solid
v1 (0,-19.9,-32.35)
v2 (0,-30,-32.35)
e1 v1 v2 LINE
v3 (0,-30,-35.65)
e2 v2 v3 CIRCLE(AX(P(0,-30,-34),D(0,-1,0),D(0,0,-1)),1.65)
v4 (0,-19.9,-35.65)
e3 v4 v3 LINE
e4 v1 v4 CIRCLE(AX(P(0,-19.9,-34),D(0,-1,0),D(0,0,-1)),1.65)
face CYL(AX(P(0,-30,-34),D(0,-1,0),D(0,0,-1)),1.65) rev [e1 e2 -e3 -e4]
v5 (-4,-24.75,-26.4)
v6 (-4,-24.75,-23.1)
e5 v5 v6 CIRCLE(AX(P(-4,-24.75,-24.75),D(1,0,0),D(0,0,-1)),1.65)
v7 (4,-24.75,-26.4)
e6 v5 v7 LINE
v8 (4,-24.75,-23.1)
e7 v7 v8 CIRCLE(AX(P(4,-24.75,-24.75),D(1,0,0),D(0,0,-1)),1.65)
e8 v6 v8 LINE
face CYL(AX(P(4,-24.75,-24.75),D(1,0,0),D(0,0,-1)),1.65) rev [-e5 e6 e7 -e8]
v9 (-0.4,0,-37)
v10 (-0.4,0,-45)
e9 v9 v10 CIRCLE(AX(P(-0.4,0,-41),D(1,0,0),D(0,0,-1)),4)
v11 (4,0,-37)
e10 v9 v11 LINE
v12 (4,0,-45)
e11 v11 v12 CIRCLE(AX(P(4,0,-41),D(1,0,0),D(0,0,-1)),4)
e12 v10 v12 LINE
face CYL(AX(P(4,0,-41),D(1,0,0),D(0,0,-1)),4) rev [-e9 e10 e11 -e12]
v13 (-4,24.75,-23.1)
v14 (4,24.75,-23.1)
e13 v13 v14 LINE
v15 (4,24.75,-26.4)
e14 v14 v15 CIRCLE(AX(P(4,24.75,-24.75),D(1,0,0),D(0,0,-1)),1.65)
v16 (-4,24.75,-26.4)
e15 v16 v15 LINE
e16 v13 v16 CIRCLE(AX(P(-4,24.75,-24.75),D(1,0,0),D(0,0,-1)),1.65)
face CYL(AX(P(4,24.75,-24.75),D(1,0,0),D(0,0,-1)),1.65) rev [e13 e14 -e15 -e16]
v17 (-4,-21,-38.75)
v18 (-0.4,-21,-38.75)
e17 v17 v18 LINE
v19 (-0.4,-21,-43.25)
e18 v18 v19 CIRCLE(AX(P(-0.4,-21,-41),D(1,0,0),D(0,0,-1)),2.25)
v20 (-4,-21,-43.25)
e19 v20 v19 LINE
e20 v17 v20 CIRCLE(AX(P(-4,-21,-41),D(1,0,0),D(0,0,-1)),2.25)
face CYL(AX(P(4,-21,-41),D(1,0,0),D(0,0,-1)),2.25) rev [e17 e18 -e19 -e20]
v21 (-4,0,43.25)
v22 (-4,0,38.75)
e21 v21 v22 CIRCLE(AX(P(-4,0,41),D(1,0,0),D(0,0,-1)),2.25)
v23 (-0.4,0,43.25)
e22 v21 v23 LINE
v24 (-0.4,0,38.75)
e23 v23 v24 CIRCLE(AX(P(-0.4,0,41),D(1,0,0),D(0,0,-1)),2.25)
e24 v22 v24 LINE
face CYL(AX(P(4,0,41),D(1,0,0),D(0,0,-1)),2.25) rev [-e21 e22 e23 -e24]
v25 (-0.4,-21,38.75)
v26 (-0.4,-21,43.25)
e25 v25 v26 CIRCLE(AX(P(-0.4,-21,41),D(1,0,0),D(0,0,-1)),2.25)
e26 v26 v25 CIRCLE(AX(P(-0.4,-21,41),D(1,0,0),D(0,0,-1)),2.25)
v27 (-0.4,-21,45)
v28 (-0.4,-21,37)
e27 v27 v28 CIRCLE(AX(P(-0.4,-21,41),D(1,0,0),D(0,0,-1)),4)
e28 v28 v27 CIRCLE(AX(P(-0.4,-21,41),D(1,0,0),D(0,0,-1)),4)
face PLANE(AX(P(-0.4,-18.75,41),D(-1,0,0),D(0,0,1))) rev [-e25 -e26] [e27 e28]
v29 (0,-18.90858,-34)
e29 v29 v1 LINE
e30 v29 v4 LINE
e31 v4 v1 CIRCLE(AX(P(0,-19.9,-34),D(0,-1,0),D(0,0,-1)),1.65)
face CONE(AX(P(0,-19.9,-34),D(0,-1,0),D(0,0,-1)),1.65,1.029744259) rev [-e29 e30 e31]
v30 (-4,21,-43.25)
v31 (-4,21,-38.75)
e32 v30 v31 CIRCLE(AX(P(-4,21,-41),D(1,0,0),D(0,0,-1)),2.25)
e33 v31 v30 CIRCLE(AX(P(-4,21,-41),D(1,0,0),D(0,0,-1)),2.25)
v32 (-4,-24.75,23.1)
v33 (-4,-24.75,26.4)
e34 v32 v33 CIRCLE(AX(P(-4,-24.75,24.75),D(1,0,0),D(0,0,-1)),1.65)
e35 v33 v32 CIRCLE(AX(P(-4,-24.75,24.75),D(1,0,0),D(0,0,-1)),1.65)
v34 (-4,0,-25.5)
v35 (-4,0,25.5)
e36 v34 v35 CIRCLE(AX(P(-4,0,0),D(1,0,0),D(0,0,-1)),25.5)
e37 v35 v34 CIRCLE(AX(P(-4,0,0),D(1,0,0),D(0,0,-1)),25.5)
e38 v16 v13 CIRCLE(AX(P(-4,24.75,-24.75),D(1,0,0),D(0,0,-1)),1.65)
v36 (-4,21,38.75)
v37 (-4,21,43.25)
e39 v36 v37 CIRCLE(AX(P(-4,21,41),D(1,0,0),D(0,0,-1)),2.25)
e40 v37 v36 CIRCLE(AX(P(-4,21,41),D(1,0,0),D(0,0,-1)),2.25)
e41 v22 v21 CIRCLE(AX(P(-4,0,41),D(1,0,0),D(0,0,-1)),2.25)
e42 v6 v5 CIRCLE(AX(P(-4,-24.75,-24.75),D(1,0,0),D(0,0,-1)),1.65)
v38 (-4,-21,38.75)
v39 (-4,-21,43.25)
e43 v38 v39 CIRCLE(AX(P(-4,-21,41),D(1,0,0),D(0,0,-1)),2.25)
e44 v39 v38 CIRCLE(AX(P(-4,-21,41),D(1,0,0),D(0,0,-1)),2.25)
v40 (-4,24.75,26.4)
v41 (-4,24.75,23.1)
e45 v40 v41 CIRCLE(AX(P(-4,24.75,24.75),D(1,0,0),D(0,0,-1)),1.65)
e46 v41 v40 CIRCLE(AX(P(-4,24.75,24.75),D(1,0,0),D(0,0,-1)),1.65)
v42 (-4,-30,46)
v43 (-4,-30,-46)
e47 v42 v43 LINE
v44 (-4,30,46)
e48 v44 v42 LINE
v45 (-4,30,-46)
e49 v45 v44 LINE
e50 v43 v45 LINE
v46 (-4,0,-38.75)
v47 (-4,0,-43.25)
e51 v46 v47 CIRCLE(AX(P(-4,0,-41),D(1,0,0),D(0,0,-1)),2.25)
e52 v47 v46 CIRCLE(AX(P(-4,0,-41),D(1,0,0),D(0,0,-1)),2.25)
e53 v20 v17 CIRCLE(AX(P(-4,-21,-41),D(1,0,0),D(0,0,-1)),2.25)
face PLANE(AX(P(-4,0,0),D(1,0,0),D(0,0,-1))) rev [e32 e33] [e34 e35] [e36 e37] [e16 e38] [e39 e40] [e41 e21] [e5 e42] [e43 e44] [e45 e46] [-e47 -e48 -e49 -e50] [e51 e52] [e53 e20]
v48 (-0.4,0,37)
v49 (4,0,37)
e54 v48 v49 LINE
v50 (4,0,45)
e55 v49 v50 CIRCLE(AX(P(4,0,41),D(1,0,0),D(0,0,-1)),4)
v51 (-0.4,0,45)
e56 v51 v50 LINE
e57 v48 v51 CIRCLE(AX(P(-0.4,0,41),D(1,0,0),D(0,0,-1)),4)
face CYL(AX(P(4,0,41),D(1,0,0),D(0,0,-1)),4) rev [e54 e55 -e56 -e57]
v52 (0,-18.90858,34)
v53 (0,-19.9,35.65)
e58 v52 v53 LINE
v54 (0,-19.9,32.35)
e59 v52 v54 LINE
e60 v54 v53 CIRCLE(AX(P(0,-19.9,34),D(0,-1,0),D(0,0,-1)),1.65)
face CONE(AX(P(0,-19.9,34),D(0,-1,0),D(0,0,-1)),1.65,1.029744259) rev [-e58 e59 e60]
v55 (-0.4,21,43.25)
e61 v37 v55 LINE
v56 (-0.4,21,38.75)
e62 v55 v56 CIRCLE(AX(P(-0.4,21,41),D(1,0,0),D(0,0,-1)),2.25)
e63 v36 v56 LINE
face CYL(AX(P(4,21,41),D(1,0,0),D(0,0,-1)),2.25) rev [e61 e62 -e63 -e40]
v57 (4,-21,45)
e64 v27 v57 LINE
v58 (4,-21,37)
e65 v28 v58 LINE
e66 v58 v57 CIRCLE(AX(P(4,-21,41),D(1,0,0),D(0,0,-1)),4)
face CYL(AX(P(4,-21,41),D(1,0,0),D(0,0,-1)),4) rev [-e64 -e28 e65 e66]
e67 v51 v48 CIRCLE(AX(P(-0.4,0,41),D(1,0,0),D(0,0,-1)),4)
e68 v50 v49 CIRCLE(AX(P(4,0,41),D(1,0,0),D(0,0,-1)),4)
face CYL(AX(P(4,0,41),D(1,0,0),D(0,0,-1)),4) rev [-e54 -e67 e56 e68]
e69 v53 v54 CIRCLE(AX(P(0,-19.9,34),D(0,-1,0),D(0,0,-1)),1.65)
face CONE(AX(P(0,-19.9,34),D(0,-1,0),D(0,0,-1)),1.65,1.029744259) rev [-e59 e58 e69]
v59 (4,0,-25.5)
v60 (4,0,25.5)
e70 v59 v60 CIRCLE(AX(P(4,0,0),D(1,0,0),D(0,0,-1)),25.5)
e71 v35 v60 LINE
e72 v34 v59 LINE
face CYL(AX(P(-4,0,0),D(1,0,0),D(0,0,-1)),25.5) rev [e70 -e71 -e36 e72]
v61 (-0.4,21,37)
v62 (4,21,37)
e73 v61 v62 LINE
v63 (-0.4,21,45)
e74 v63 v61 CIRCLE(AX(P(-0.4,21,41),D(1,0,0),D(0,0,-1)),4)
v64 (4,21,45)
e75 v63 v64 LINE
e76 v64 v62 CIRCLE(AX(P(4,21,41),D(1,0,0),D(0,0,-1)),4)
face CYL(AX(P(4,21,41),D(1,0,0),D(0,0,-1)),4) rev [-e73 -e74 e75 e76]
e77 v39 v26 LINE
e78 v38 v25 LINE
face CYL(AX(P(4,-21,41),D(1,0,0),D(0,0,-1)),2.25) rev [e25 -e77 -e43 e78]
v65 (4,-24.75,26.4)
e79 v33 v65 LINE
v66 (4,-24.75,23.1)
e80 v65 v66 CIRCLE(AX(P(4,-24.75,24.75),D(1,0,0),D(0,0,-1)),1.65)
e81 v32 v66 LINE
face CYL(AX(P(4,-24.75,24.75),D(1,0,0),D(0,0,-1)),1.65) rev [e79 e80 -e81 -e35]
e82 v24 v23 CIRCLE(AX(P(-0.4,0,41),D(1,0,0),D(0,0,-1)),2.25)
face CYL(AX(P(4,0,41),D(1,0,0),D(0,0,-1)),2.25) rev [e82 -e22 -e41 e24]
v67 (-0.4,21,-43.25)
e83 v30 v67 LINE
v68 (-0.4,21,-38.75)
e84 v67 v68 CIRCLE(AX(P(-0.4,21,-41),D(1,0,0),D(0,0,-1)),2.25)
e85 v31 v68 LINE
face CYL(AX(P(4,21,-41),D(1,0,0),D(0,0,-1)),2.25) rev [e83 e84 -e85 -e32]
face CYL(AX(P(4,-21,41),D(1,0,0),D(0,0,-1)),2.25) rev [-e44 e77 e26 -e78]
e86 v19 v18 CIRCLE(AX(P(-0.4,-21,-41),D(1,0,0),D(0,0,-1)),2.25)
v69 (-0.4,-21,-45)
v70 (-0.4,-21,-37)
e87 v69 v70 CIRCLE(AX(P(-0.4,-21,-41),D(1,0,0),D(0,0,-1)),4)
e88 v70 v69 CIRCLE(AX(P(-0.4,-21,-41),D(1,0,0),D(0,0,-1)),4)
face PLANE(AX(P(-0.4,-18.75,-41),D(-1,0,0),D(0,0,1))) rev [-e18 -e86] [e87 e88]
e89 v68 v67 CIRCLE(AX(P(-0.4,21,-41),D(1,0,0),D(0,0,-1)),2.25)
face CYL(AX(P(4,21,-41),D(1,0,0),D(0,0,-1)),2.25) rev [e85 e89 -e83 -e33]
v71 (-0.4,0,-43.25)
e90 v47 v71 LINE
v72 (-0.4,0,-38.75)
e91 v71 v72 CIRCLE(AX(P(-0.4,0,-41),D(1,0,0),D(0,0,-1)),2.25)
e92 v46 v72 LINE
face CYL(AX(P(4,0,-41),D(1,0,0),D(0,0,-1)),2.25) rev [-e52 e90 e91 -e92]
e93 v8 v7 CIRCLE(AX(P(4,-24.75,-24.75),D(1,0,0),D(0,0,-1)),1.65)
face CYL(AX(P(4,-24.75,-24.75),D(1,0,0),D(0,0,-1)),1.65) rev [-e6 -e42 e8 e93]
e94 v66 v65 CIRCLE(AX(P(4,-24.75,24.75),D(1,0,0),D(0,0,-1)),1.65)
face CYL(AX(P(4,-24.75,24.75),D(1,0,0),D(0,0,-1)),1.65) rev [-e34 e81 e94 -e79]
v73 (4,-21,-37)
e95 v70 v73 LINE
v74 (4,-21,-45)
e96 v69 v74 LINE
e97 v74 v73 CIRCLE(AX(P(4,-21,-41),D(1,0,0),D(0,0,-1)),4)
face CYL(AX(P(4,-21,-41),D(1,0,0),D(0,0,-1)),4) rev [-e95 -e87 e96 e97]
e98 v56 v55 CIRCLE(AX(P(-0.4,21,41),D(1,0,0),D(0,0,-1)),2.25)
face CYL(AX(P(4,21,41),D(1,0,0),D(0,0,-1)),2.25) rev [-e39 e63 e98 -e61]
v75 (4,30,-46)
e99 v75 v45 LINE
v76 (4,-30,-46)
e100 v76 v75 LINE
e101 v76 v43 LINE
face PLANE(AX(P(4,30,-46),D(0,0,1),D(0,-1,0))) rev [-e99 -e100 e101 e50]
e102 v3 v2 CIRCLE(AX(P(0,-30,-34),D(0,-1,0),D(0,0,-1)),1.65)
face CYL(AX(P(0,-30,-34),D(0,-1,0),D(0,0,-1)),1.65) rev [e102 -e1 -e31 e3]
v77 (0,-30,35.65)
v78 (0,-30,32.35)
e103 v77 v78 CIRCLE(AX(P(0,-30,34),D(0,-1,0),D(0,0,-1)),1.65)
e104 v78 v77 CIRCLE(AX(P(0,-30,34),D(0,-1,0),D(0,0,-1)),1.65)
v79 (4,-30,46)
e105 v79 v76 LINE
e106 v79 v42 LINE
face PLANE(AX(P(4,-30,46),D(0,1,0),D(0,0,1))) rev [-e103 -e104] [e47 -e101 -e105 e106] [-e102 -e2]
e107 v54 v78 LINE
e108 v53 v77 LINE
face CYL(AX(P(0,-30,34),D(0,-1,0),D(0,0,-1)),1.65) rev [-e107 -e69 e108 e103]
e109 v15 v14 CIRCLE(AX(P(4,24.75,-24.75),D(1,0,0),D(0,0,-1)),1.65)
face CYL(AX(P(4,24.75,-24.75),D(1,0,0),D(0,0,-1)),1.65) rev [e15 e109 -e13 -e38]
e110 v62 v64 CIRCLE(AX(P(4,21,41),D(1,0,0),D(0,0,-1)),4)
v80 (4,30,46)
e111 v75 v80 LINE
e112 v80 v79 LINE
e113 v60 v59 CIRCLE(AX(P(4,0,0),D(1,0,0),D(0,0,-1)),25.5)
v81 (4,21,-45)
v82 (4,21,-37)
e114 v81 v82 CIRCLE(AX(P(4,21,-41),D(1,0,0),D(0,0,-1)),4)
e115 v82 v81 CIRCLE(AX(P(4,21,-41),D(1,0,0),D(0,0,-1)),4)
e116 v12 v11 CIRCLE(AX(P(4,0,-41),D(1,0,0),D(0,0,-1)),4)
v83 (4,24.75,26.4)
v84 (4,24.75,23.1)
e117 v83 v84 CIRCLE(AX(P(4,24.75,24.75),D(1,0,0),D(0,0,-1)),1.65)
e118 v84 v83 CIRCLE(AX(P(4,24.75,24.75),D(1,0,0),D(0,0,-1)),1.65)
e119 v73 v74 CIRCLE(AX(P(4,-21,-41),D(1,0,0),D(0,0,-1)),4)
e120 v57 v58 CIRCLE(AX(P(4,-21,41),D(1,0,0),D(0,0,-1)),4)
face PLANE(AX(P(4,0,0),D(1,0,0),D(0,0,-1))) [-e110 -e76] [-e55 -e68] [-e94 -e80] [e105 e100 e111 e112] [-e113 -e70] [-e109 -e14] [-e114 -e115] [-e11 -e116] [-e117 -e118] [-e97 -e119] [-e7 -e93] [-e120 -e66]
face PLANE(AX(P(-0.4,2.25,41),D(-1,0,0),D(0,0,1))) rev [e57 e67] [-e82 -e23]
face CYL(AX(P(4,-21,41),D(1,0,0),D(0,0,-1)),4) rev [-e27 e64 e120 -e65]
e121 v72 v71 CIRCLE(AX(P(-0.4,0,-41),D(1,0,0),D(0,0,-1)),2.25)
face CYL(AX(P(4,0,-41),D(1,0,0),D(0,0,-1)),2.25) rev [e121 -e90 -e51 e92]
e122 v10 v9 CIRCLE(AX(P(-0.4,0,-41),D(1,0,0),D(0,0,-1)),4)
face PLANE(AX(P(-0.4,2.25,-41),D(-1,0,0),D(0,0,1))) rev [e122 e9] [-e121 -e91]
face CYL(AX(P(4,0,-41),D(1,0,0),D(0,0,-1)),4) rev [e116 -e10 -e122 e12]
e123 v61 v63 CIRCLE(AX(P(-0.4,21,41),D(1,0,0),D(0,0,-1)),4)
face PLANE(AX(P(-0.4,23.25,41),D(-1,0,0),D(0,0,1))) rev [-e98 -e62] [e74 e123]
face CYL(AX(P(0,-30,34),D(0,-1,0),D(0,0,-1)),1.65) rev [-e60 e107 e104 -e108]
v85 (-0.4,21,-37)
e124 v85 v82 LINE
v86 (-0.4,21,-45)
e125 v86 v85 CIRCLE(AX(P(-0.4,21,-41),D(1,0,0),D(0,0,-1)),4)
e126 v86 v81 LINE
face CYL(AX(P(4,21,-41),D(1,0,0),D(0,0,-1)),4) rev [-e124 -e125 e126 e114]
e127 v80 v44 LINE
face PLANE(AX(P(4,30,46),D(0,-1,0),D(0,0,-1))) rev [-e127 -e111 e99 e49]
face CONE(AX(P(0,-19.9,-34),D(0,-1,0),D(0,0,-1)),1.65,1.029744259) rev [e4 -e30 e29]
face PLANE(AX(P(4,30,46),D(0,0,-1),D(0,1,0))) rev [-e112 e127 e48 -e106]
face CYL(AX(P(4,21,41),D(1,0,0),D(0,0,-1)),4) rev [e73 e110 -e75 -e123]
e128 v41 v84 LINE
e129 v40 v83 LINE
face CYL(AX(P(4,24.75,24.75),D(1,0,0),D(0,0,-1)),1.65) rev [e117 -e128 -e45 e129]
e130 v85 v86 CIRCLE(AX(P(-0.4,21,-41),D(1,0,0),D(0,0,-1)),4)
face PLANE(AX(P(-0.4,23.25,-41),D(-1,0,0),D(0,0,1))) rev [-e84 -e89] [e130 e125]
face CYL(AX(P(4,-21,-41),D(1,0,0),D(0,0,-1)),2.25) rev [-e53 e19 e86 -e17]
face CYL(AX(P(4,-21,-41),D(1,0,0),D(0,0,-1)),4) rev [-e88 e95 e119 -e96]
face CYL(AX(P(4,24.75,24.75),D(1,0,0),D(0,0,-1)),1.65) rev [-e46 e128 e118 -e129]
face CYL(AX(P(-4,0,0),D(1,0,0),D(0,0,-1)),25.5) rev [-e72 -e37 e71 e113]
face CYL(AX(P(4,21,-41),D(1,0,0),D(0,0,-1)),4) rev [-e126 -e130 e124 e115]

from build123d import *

# Parameters (mm, degrees)
SKETCH1_W                                           = 92
SKETCH1_H                                           = 60
BOSS_EXTRUDE1_DEPTH                                 = 4
M4_TAPPED_HOLE1_D                                   = 3.3
M4_TAPPED_HOLE1_DEPTH                               = 10.1
M4_TAPPED_HOLE1_TIP                                 = 0.991420021
SKETCH4_R                                           = 25.5
CUT_EXTRUDE1_DEPTH                                  = 56.497747702
CBORE_FOR_M4_HEX_SOCKET_HEAD_CAP_SCREW1_D           = 4.5
CBORE_FOR_M4_HEX_SOCKET_HEAD_CAP_SCREW1_CBORE_D     = 8
CBORE_FOR_M4_HEX_SOCKET_HEAD_CAP_SCREW1_CBORE_DEPTH = 4.4
M4_TAPPED_HOLE2_D                                   = 3.3
M4_TAPPED_HOLE2_DEPTH                               = 10.1
M4_TAPPED_HOLE2_TIP                                 = 0.991420021


with BuildPart() as part:
    # Sketch1 → Boss-Extrude1 (new, symmetric)
    with BuildSketch(Plane(origin=(0, 0, 0), x_dir=(0, 0, -1), z_dir=(1, 0, 0))):
        Rectangle(SKETCH1_W, SKETCH1_H)
    extrude(amount=BOSS_EXTRUDE1_DEPTH, both=True)

    # M4 Tapped Hole1
    with Locations(Plane(origin=(4, 0, 0), x_dir=(0, 0, -1), z_dir=(1, 0, 0))):
        with Locations((-24.75, 24.75), (24.75, 24.75), (-24.75, -24.75), (24.75, -24.75)):
            Hole(M4_TAPPED_HOLE1_D / 2, depth=M4_TAPPED_HOLE1_DEPTH)
            with Locations((0, 0, -(M4_TAPPED_HOLE1_DEPTH + M4_TAPPED_HOLE1_TIP / 2))):  # 118° drill point
                Cone(0, M4_TAPPED_HOLE1_D / 2, M4_TAPPED_HOLE1_TIP, mode=Mode.SUBTRACT)

    # Sketch4 → Cut-Extrude1 (cut, through all)
    with BuildSketch(Plane(origin=(4, 0, 0), x_dir=(0, 0, -1), z_dir=(1, 0, 0))):
        Circle(SKETCH4_R)
    extrude(amount=-CUT_EXTRUDE1_DEPTH, mode=Mode.SUBTRACT)

    # CBORE for M4 Hex Socket Head Cap Screw1 (through all)
    with Locations(Plane(origin=(4, 0, 0), x_dir=(0, 0, -1), z_dir=(1, 0, 0))):
        with Locations((-41, 21), (-41, 0), (-41, -21), (41, 21), (41, 0), (41, -21)):
            CounterBoreHole(CBORE_FOR_M4_HEX_SOCKET_HEAD_CAP_SCREW1_D / 2, CBORE_FOR_M4_HEX_SOCKET_HEAD_CAP_SCREW1_CBORE_D / 2, CBORE_FOR_M4_HEX_SOCKET_HEAD_CAP_SCREW1_CBORE_DEPTH)

    # M4 Tapped Hole2
    with Locations(Plane(origin=(0, -30, 0), x_dir=(-1, 0, 0), z_dir=(0, -1, 0))):
        with Locations((0, -34), (0, 34)):
            Hole(M4_TAPPED_HOLE2_D / 2, depth=M4_TAPPED_HOLE2_DEPTH)
            with Locations((0, 0, -(M4_TAPPED_HOLE2_DEPTH + M4_TAPPED_HOLE2_TIP / 2))):  # 118° drill point
                Cone(0, M4_TAPPED_HOLE2_D / 2, M4_TAPPED_HOLE2_TIP, mode=Mode.SUBTRACT)


solid = part.part
